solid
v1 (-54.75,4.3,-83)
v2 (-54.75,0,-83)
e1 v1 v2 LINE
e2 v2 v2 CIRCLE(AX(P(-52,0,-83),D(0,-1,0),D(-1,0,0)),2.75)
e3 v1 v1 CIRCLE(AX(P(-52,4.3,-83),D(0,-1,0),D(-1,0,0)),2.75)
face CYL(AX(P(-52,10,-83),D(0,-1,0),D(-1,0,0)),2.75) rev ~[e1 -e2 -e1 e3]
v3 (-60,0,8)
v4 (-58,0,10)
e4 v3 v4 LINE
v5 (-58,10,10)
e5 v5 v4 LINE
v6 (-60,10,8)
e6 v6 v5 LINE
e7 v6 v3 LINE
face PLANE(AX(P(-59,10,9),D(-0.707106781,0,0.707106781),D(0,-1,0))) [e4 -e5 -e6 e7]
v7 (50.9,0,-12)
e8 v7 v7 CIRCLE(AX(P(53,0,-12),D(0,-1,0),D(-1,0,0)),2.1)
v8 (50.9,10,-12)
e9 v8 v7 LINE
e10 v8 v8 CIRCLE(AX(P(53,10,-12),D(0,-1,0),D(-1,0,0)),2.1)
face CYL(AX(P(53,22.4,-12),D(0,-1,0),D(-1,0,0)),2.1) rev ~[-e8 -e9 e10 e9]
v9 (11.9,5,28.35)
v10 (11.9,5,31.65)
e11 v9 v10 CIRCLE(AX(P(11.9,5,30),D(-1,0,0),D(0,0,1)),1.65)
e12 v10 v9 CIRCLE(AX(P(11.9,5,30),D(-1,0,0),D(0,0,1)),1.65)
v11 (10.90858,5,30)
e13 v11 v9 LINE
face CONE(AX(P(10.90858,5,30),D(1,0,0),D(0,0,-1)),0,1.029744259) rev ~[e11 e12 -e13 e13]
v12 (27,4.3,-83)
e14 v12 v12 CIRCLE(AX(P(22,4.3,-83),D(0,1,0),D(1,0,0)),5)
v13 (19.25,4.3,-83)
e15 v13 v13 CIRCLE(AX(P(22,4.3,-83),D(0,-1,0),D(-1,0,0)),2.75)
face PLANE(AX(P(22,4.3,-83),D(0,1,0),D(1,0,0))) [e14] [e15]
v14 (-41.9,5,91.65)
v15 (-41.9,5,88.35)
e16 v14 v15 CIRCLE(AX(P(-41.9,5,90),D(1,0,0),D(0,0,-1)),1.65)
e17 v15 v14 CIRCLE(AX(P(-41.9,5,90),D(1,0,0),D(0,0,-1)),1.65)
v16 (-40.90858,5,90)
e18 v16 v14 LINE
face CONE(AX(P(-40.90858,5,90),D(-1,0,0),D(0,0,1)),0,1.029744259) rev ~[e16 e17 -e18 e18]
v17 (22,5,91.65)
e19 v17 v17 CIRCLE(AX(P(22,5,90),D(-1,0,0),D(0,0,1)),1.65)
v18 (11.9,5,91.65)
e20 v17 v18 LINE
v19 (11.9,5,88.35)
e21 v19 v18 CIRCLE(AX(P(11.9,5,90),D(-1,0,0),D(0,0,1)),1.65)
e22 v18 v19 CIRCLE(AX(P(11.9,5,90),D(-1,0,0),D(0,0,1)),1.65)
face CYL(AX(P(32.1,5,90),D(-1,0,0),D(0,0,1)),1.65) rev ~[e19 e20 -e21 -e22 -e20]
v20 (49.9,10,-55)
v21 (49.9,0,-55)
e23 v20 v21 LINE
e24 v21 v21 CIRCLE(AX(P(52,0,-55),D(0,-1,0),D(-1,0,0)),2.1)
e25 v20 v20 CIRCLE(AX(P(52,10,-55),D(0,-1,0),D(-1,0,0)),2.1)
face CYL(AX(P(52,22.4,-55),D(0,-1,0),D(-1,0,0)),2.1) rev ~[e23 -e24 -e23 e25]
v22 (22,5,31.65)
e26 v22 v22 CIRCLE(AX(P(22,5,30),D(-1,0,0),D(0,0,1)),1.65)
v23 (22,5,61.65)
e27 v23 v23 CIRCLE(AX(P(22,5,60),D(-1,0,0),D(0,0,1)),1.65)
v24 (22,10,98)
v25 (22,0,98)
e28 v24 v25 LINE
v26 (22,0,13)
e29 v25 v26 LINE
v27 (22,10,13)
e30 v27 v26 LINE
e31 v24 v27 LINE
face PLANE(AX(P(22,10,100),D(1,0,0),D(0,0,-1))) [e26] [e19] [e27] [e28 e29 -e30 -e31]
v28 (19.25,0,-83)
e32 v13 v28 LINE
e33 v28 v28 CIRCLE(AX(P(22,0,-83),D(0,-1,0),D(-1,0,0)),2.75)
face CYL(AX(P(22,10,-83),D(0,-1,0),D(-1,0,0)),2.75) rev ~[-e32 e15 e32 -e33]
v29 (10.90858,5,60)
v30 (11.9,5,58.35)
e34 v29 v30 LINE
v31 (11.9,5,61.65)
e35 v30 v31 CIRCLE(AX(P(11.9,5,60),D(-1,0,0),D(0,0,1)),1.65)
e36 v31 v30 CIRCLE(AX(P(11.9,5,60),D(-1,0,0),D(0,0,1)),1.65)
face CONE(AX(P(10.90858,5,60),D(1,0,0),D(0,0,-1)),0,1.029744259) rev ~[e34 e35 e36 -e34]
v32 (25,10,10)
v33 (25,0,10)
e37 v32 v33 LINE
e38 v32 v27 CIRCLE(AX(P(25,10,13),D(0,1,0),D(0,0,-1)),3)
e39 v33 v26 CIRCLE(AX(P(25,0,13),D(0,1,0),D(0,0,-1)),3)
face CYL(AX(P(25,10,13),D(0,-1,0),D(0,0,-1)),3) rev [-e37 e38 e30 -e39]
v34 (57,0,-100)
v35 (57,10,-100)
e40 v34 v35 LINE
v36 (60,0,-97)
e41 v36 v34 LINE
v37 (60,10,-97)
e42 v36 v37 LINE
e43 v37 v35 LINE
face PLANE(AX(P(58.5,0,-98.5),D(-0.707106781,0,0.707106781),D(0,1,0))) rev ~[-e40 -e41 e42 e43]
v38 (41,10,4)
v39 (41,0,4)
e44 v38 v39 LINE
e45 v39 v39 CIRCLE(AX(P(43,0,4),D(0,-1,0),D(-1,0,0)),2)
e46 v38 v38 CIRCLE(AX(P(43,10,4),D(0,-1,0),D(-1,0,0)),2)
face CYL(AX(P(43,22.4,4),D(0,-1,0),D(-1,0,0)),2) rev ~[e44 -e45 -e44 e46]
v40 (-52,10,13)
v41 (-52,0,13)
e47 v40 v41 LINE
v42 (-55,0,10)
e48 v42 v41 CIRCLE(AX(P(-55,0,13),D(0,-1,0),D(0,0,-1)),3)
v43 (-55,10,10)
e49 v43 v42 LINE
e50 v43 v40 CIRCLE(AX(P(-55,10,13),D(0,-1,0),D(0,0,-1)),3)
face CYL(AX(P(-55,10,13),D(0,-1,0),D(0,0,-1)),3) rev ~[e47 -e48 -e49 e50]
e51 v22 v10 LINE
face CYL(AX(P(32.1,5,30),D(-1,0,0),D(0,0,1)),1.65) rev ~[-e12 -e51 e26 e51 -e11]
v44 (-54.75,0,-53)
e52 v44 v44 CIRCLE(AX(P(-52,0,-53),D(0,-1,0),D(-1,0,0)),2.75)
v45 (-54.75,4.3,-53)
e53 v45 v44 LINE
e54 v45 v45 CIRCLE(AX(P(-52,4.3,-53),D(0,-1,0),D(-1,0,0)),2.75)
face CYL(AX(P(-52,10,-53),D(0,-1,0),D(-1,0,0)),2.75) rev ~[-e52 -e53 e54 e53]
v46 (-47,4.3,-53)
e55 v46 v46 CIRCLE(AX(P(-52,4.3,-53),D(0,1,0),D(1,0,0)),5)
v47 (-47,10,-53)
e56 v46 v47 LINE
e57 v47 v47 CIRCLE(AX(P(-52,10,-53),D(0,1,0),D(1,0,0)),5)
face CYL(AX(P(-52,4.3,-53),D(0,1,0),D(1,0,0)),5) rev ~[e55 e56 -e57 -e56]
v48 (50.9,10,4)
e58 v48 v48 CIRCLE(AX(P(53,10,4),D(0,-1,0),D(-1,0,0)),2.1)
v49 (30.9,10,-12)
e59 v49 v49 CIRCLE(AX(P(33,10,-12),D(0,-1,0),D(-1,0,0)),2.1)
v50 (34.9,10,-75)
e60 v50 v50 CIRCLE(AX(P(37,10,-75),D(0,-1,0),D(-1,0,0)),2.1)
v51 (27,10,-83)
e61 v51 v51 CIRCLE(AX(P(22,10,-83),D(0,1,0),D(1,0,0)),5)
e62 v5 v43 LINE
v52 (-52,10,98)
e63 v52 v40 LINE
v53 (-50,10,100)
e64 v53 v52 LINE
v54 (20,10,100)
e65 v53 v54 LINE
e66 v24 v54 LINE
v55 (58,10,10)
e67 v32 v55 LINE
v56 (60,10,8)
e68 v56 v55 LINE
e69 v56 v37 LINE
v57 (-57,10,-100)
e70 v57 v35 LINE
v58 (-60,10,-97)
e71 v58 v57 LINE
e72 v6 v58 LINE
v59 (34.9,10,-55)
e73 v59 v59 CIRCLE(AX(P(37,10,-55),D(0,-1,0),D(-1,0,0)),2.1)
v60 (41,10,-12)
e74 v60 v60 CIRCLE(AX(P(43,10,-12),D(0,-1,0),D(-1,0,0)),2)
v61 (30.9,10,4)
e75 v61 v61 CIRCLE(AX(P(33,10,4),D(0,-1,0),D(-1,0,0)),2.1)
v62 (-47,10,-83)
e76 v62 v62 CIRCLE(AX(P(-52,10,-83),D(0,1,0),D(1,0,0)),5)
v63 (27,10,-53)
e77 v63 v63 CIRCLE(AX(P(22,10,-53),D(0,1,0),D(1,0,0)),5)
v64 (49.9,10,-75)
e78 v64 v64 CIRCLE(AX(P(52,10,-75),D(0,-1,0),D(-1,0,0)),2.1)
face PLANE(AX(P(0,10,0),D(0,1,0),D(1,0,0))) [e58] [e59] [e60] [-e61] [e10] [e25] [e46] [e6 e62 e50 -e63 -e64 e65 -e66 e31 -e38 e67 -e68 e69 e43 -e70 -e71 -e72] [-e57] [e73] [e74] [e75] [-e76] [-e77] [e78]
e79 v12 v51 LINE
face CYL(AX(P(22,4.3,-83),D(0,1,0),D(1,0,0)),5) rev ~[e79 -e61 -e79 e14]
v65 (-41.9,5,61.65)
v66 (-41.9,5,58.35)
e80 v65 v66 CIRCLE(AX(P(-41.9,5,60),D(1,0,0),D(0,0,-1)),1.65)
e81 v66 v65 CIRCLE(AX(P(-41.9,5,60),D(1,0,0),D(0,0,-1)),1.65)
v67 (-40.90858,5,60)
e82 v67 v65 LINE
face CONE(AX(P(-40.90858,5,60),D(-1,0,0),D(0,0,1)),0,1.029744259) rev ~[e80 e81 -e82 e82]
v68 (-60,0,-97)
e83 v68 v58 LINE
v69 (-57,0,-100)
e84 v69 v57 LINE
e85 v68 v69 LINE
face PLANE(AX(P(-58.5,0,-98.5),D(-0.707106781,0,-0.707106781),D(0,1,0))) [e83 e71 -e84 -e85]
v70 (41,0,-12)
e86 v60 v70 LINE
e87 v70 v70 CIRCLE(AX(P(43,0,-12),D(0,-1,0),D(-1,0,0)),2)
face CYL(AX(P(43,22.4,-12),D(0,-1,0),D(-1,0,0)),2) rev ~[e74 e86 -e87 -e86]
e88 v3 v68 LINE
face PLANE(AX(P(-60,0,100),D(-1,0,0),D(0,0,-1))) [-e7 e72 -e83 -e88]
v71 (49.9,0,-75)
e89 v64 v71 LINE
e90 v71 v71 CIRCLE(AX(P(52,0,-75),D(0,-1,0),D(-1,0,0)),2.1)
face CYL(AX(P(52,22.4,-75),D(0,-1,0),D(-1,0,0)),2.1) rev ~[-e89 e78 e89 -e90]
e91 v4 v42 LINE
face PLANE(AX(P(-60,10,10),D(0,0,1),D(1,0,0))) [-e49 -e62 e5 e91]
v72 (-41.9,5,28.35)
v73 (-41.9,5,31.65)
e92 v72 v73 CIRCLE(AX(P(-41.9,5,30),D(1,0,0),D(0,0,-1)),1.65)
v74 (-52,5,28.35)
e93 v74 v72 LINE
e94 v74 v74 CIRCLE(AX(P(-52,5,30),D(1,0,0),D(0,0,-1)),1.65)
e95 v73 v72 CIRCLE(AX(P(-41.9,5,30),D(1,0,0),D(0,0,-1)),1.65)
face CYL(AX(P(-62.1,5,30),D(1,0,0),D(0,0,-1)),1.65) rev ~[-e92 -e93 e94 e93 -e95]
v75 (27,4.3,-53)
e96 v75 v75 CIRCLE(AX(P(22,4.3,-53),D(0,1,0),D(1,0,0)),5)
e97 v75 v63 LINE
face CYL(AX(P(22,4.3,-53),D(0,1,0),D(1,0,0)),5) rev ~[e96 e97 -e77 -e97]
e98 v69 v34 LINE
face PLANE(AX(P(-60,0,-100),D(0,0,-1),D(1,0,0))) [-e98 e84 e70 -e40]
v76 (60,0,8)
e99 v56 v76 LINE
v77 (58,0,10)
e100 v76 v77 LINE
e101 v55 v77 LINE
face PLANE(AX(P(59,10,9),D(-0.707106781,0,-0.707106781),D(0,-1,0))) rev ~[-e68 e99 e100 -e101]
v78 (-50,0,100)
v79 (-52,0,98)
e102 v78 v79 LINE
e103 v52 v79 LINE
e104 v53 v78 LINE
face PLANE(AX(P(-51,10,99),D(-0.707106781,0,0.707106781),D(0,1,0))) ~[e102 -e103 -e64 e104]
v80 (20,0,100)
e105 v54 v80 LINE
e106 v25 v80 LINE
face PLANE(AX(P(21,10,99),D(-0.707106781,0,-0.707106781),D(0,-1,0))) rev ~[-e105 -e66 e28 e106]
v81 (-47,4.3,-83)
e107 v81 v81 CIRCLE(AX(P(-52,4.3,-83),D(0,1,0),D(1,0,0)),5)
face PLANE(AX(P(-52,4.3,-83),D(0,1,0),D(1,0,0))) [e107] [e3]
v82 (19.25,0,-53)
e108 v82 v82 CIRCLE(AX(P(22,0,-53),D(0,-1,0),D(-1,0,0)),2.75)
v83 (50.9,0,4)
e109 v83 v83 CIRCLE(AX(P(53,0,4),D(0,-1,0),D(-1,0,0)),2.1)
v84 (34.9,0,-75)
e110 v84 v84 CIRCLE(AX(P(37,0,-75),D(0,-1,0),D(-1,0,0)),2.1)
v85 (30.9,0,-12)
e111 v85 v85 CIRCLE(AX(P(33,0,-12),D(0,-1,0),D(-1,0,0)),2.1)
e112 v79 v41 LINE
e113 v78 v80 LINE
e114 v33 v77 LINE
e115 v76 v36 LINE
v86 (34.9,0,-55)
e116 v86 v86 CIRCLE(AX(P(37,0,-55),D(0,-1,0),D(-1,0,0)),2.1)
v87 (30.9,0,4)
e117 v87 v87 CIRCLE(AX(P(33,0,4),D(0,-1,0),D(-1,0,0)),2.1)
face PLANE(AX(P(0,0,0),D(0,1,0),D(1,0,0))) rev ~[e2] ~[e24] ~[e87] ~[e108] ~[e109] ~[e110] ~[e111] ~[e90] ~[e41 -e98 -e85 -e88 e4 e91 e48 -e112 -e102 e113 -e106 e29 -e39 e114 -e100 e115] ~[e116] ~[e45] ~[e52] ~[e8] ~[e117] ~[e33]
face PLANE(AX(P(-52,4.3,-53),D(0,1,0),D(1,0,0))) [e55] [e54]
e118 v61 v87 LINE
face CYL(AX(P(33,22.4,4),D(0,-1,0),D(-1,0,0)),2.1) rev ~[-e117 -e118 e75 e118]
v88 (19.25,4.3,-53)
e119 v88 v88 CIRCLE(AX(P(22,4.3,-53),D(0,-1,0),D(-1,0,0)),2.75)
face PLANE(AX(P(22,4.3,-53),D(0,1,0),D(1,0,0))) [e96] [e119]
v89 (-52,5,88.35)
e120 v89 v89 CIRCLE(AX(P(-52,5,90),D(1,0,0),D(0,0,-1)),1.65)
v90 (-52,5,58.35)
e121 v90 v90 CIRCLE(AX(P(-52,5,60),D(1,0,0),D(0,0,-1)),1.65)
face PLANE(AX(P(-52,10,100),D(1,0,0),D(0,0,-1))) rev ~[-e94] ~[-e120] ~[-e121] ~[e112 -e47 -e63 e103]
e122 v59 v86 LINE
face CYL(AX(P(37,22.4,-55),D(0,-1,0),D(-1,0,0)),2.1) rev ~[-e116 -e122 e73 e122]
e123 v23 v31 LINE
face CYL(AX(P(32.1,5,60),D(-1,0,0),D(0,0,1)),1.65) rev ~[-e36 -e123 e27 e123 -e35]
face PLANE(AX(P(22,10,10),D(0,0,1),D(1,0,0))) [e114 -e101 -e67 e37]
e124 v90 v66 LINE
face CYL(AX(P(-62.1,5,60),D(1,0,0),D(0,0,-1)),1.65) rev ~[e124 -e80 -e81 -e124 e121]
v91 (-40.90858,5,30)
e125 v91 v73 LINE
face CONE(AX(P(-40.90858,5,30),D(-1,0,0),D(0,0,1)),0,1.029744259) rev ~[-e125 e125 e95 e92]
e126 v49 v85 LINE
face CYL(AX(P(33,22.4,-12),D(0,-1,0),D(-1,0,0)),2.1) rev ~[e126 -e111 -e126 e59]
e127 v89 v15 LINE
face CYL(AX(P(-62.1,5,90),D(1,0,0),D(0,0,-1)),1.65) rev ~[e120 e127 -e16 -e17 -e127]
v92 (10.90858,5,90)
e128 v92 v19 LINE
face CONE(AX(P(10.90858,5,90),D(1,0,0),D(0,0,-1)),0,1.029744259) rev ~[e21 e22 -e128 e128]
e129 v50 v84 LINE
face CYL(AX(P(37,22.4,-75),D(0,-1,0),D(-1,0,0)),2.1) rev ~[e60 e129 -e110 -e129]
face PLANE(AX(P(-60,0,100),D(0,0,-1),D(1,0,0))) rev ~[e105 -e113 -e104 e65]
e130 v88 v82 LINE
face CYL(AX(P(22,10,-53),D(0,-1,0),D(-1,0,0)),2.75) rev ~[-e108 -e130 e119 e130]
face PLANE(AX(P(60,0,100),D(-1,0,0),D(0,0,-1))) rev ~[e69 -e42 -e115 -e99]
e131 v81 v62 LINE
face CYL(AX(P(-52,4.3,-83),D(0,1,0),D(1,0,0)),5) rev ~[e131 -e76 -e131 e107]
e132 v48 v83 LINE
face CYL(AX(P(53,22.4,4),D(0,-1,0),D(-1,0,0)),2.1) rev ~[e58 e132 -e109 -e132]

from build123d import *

# Parameters (mm, degrees)
SKETCH_1_W                = 120
SKETCH_1_H                = 200
EXTRUDE_1_DEPTH           = 10
CHAMFER_1_SIZE            = 3
HOLE_WIZARD_0_D           = 5.5
HOLE_WIZARD_0_DEPTH       = 10.1
HOLE_WIZARD_0_CBORE_D     = 10
HOLE_WIZARD_0_CBORE_DEPTH = 5.7
HOLE_WIZARD_0_TIP         = 1.652366702
SKETCH_4_W                = 38
SKETCH_4_H                = 90
SKETCH_4_W_2              = 8
CUT_EXTRUDE_1_DEPTH       = 20
CHAMFER_2_SIZE            = 2
FILLET_1_R                = 3
HOLE_WIZARD_M4_1_D        = 3.3
HOLE_WIZARD_M4_1_DEPTH    = 10.1
HOLE_WIZARD_M4_1_TIP      = 0.991420021
HOLE_WIZARD_M4_2_D        = 3.3
HOLE_WIZARD_M4_2_DEPTH    = 10.1
HOLE_WIZARD_M4_2_TIP      = 0.991420021
MM_2_D                    = 4
MM_2_DEPTH                = 12.4
MM_2_TIP                  = 1.201721238
HOLE_WIZARD_M5_2_D        = 4.2
HOLE_WIZARD_M5_2_DEPTH    = 12.4
HOLE_WIZARD_M5_2_TIP      = 1.2618073
HOLE_WIZARD_M5_3_D        = 4.2
HOLE_WIZARD_M5_3_DEPTH    = 12.4
HOLE_WIZARD_M5_3_TIP      = 1.2618073


with BuildPart() as part:
    # 草图1 → 凸台-拉伸1 (new body)
    with BuildSketch(Plane(origin=(0, 0, 0), x_dir=(1, 0, 0), z_dir=(0, 1, 0))):
        Rectangle(SKETCH_1_W, SKETCH_1_H)
    extrude(amount=EXTRUDE_1_DEPTH)

    # 倒角1
    chamfer_1_edges = [part.edges().sort_by_distance(p)[0] for p in [
        (60, 5, 100),
        (-60, 5, 100),
        (-60, 5, -100),
        (60, 5, -100),
    ]]
    chamfer(chamfer_1_edges, length=CHAMFER_1_SIZE)

    # 打孔尺寸(%根据)内六角圆柱头螺钉的类型0
    with Locations(Plane(origin=(0, 10, 0), x_dir=(1, 0, 0), z_dir=(0, 1, 0))):
        with Locations((-52, 83), (-52, 53), (22, 53), (22, 83)):
            CounterBoreHole(HOLE_WIZARD_0_D / 2, HOLE_WIZARD_0_CBORE_D / 2, HOLE_WIZARD_0_CBORE_DEPTH, depth=HOLE_WIZARD_0_DEPTH)
            with Locations((0, 0, -(HOLE_WIZARD_0_DEPTH + HOLE_WIZARD_0_TIP / 2))):  # 118° drill point
                Cone(0, HOLE_WIZARD_0_D / 2, HOLE_WIZARD_0_TIP, mode=Mode.SUBTRACT)

    # 草图4 → 切除-拉伸1 (cut)
    with BuildSketch(Plane(origin=(0, 10, 0), x_dir=(1, 0, 0), z_dir=(0, 1, 0))):
        with Locations((41, -55)):
            Rectangle(SKETCH_4_W, SKETCH_4_H)
        with Locations((-56, -55)):
            Rectangle(SKETCH_4_W_2, SKETCH_4_H)
    extrude(amount=-CUT_EXTRUDE_1_DEPTH, mode=Mode.SUBTRACT)

    # 倒角2
    chamfer_2_edges = [part.edges().sort_by_distance(p)[0] for p in [
        (22, 5, 100),
        (60, 5, 10),
        (-60, 5, 10),
        (-52, 5, 100),
    ]]
    chamfer(chamfer_2_edges, length=CHAMFER_2_SIZE)

    # 圆角1
    fillet_1_edges = [part.edges().sort_by_distance(p)[0] for p in [
        (22, 5, 10),
        (-52, 5, 10),
    ]]
    fillet(fillet_1_edges, radius=FILLET_1_R)

    # M4 螺纹孔1
    with Locations(Plane.ZY.offset(52)):
        with Locations((30, 5), (60, 5), (90, 5)):
            Hole(HOLE_WIZARD_M4_1_D / 2, depth=HOLE_WIZARD_M4_1_DEPTH)
            with Locations((0, 0, -(HOLE_WIZARD_M4_1_DEPTH + HOLE_WIZARD_M4_1_TIP / 2))):  # 118° drill point
                Cone(0, HOLE_WIZARD_M4_1_D / 2, HOLE_WIZARD_M4_1_TIP, mode=Mode.SUBTRACT)

    # M4 螺纹孔2
    with Locations(Plane(origin=(22, 0, 0), x_dir=(0, 0, -1), z_dir=(1, 0, 0))):
        with Locations((-30, 5), (-60, 5), (-90, 5)):
            Hole(HOLE_WIZARD_M4_2_D / 2, depth=HOLE_WIZARD_M4_2_DEPTH)
            with Locations((0, 0, -(HOLE_WIZARD_M4_2_DEPTH + HOLE_WIZARD_M4_2_TIP / 2))):  # 118° drill point
                Cone(0, HOLE_WIZARD_M4_2_D / 2, HOLE_WIZARD_M4_2_TIP, mode=Mode.SUBTRACT)

    # 大小mm 暗销孔2
    with Locations(Plane(origin=(0, 10, 0), x_dir=(1, 0, 0), z_dir=(0, 1, 0))):
        with Locations((43, 12), (43, -4)):
            Hole(MM_2_D / 2, depth=MM_2_DEPTH)
            with Locations((0, 0, -(MM_2_DEPTH + MM_2_TIP / 2))):  # 118° drill point
                Cone(0, MM_2_D / 2, MM_2_TIP, mode=Mode.SUBTRACT)

    # M5 螺纹孔2
    with Locations(Plane(origin=(0, 10, 0), x_dir=(1, 0, 0), z_dir=(0, 1, 0))):
        with Locations((53, -4), (33, -4), (53, 12), (33, 12)):
            Hole(HOLE_WIZARD_M5_2_D / 2, depth=HOLE_WIZARD_M5_2_DEPTH)
            with Locations((0, 0, -(HOLE_WIZARD_M5_2_DEPTH + HOLE_WIZARD_M5_2_TIP / 2))):  # 118° drill point
                Cone(0, HOLE_WIZARD_M5_2_D / 2, HOLE_WIZARD_M5_2_TIP, mode=Mode.SUBTRACT)

    # M5 螺纹孔3
    with Locations(Plane(origin=(0, 10, 0), x_dir=(1, 0, 0), z_dir=(0, 1, 0))):
        with Locations((52, 55), (37, 55), (52, 75), (37, 75)):
            Hole(HOLE_WIZARD_M5_3_D / 2, depth=HOLE_WIZARD_M5_3_DEPTH)
            with Locations((0, 0, -(HOLE_WIZARD_M5_3_DEPTH + HOLE_WIZARD_M5_3_TIP / 2))):  # 118° drill point
                Cone(0, HOLE_WIZARD_M5_3_D / 2, HOLE_WIZARD_M5_3_TIP, mode=Mode.SUBTRACT)


solid = part.part
